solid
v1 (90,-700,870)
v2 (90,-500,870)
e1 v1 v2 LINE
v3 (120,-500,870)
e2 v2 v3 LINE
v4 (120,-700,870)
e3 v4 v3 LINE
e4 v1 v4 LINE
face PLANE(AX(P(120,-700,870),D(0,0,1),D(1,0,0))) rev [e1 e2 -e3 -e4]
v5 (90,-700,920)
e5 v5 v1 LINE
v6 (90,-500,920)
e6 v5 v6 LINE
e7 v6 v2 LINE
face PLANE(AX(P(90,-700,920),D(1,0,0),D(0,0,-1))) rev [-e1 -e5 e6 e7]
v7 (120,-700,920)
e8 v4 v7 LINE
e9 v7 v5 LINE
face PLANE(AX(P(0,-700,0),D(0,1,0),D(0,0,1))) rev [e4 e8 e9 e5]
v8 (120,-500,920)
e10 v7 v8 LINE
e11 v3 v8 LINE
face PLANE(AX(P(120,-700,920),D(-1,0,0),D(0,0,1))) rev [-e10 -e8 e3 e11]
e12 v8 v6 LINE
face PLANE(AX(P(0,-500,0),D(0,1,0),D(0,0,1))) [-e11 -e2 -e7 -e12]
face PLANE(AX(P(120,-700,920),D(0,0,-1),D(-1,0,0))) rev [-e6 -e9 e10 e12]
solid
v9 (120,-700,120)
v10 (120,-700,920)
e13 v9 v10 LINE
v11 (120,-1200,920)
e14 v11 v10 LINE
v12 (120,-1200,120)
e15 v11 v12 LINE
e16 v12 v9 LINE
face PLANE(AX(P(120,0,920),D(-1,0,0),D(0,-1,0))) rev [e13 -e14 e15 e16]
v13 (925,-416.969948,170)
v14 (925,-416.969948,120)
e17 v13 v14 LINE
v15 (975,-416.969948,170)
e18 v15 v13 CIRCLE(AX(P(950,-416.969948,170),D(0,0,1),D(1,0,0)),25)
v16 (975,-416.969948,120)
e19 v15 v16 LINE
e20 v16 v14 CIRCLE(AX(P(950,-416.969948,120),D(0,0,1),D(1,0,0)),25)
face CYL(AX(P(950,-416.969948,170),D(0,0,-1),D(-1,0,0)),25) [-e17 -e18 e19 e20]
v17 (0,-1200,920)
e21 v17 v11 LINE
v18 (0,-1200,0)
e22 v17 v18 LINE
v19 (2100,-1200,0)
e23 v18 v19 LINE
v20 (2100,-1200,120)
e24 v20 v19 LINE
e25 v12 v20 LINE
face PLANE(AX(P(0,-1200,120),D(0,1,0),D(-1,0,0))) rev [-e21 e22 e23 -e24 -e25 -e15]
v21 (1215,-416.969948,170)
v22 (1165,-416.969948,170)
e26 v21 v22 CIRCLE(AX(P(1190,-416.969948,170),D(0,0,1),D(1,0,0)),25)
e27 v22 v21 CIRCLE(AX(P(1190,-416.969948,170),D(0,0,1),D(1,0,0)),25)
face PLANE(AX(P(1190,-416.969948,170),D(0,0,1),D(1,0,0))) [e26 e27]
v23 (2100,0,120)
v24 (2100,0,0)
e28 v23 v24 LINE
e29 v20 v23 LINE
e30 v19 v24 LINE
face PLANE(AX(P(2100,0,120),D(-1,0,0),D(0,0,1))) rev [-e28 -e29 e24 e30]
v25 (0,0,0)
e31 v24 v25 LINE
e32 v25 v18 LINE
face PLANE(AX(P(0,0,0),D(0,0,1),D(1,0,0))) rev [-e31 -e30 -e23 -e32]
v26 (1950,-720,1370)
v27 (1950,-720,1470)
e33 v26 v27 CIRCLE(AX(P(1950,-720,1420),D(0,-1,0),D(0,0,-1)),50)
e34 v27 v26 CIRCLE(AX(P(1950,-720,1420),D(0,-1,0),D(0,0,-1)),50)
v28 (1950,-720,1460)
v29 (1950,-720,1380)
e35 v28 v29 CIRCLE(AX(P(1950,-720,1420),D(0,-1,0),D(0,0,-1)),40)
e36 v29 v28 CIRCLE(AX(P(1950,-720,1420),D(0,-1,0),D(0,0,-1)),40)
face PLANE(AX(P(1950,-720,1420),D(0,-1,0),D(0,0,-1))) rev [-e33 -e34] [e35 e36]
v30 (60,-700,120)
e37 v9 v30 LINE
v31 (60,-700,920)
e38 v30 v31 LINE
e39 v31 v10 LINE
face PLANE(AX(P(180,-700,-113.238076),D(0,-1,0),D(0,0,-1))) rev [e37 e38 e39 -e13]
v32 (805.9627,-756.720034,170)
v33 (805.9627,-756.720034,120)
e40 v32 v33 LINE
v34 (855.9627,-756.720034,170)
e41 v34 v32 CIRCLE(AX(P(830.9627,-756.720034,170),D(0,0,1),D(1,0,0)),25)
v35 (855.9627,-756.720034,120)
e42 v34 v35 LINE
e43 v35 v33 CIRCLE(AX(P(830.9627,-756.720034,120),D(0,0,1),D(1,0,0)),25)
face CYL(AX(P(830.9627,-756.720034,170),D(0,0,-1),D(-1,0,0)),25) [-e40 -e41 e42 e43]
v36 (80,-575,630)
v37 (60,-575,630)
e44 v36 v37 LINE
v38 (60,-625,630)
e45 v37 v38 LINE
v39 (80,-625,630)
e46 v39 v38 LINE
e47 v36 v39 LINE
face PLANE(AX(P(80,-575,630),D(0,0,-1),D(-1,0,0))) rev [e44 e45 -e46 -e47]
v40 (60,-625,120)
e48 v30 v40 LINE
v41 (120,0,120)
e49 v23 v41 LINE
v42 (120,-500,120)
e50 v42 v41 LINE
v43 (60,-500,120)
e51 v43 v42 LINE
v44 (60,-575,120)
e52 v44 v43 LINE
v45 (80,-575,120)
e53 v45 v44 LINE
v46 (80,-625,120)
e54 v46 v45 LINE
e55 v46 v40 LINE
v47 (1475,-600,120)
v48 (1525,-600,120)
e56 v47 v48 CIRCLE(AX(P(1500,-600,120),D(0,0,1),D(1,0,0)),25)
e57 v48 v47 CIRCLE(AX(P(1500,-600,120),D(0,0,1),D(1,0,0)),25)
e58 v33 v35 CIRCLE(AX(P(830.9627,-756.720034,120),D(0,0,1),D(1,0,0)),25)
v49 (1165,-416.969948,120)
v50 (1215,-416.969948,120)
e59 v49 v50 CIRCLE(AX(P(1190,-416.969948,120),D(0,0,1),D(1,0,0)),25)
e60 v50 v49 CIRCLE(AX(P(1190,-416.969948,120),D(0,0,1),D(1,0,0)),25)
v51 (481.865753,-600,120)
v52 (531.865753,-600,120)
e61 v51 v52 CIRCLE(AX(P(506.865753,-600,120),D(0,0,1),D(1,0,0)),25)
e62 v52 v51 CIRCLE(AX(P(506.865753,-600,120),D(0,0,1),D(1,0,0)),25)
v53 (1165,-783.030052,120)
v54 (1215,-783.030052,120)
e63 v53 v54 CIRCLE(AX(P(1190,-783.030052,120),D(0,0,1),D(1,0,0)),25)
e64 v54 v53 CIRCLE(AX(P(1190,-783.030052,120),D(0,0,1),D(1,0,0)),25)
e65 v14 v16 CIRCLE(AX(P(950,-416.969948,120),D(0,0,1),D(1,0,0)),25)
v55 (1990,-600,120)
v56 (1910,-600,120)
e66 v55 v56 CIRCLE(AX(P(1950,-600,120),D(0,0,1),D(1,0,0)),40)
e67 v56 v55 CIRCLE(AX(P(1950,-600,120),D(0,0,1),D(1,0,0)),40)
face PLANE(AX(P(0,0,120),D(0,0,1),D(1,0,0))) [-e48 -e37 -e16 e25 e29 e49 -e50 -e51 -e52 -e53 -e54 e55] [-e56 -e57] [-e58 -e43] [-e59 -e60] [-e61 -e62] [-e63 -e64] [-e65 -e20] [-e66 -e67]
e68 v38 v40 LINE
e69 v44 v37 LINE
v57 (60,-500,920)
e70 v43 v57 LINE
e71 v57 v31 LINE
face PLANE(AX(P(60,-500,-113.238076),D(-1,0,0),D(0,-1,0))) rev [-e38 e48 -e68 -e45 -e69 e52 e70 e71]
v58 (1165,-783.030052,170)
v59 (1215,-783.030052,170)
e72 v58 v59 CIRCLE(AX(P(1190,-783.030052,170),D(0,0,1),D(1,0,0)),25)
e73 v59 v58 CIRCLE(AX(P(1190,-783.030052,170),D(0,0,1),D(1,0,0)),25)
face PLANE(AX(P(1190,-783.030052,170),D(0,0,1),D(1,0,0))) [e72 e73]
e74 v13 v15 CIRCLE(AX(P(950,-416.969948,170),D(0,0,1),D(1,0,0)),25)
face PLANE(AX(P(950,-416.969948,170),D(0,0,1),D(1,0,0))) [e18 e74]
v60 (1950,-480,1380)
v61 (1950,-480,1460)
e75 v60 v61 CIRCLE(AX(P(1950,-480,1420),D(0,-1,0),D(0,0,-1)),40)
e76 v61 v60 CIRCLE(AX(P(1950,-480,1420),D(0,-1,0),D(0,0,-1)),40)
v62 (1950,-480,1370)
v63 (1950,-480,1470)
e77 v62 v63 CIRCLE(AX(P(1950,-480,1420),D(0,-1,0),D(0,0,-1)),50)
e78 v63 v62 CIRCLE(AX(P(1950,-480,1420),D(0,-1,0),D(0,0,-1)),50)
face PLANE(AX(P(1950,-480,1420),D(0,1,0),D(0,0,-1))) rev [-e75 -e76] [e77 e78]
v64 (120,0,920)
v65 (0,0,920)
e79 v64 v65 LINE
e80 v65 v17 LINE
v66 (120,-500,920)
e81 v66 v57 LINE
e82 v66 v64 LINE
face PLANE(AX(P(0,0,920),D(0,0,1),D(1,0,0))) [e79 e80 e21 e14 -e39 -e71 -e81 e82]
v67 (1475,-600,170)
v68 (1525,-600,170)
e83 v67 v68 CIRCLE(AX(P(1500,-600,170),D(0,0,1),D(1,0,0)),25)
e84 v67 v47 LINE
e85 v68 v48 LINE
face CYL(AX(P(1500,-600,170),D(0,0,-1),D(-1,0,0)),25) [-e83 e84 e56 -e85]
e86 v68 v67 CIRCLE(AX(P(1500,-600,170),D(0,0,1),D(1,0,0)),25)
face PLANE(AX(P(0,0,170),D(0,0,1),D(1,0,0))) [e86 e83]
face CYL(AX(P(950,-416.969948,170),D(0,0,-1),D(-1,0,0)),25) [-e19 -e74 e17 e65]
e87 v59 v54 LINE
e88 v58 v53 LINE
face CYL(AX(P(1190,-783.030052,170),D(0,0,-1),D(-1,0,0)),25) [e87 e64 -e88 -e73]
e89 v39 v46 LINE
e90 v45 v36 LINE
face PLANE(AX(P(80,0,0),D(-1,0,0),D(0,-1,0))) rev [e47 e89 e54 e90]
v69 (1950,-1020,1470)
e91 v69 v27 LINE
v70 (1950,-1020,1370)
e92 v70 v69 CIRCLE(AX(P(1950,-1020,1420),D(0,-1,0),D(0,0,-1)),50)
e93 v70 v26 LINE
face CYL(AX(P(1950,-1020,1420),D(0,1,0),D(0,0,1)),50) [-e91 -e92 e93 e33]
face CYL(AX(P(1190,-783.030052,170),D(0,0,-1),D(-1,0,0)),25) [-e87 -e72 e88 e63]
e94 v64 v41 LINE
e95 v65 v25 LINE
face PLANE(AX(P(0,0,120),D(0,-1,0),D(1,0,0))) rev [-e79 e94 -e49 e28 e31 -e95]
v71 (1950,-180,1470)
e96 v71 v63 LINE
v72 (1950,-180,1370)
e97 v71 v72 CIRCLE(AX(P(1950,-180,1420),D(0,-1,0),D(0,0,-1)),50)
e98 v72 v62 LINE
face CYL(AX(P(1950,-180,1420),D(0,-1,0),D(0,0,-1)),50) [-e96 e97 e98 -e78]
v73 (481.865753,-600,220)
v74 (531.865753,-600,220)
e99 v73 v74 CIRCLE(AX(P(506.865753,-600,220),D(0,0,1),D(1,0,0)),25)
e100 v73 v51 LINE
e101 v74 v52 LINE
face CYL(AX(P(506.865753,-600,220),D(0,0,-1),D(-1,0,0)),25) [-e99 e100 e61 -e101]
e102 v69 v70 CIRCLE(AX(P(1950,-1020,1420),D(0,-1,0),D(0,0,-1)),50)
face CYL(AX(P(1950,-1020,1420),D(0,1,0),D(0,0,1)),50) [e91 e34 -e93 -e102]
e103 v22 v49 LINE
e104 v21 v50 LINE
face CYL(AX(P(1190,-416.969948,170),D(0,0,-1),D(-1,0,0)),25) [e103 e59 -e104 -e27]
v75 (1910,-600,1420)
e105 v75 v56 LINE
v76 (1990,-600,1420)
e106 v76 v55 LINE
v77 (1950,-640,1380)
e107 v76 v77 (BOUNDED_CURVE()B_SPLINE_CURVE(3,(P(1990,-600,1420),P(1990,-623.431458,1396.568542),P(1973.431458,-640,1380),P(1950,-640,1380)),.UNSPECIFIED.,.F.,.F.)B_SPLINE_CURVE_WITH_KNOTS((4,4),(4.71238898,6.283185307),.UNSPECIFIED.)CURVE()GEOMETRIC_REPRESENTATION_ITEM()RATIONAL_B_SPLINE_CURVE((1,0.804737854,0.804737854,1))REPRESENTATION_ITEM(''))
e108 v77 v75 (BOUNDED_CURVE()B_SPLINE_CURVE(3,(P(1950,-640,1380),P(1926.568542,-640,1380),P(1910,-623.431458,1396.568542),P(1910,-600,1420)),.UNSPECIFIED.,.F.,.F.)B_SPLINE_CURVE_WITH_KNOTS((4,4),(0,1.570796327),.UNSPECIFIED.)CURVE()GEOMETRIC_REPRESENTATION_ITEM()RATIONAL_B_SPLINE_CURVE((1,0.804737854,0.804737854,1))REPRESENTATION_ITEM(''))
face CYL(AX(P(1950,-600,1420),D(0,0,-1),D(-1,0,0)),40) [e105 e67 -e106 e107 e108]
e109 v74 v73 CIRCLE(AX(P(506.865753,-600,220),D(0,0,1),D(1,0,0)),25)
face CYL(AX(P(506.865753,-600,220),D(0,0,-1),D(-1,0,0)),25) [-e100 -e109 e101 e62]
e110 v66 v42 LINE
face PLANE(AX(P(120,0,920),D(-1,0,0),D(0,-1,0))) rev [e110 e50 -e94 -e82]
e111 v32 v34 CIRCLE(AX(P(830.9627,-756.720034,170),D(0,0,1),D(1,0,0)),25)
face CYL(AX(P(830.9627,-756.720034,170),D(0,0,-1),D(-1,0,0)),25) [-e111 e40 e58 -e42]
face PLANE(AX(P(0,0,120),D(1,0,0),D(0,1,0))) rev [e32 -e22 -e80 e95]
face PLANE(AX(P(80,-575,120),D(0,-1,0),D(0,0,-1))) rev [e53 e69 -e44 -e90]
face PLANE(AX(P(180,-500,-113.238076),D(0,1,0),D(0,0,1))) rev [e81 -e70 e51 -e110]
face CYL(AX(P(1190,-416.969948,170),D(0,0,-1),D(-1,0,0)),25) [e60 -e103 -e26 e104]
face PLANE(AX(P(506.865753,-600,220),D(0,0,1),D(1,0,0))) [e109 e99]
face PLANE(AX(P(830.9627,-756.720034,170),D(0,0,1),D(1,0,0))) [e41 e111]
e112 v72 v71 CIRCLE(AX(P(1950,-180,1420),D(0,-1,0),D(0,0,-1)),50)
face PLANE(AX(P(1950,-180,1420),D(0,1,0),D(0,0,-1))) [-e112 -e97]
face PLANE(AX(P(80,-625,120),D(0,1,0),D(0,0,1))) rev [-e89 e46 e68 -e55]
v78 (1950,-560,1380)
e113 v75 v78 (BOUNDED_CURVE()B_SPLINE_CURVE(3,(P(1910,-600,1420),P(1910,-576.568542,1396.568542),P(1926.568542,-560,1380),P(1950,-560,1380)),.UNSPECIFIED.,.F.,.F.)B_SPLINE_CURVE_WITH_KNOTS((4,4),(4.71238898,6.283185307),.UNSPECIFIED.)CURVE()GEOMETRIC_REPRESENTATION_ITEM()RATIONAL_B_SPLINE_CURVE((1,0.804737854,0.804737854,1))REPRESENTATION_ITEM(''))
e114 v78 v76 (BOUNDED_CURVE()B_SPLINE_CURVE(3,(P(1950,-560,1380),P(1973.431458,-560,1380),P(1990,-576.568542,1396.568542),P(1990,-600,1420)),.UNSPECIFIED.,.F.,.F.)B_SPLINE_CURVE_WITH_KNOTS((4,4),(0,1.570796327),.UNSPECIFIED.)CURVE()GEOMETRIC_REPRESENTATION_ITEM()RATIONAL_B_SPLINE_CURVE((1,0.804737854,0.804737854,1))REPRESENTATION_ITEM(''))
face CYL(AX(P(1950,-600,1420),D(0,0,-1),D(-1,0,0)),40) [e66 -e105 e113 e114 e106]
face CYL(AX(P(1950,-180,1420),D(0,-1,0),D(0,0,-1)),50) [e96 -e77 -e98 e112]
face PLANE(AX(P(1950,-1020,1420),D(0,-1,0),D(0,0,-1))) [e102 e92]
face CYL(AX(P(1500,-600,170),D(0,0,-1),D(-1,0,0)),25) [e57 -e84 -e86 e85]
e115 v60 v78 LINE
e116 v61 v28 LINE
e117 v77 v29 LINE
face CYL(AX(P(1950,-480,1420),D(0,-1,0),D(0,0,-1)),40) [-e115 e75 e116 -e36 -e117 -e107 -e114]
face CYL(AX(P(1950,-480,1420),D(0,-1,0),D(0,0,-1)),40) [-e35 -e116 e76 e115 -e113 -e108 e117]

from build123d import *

# Parameters (mm, degrees)
SKETCH2_W                = 2100
SKETCH2_H                = 1200
BOSS_EXTRUDE1_DEPTH      = 120
SKETCH3_W                = 120
SKETCH3_H                = 1200
BOSS_EXTRUDE2_DEPTH      = 800
SKETCH4_R                = 40
BOSS_EXTRUDE3_DEPTH      = 1300
BOSS_EXTRUDE4_DEPTH      = 120
BOSS_EXTRUDE4_DEPTH_BACK = 120
SKETCH6_R                = 40
BOSS_EXTRUDE5_START      = 120
SKETCH7_R                = 50
BOSS_EXTRUDE5_DEPTH      = 300
SKETCH9_R                = 25
BOSS_EXTRUDE6_DEPTH      = 50
SKETCH10_R               = 25
BOSS_EXTRUDE7_DEPTH      = 50
SKETCH11_R               = 25
BOSS_EXTRUDE8_DEPTH      = 50
SKETCH12_R               = 25
BOSS_EXTRUDE9_DEPTH      = 50
SKETCH13_R               = 25
BOSS_EXTRUDE10_DEPTH     = 100
SKETCH14_W               = 120
SKETCH14_H               = 200
CUT_EXTRUDE1_DEPTH       = 800
SKETCH15_W               = 510
SKETCH15_H               = 50
BOSS_EXTRUDE11_DEPTH     = 20
SKETCH16_W               = 30
SKETCH16_H               = 50
BOSS_EXTRUDE12_DEPTH     = 200


with BuildPart() as part:
    # Sketch2 → Boss-Extrude1 (new body)
    with BuildSketch(Plane.XY):
        with Locations((1050, -600)):
            Rectangle(SKETCH2_W, SKETCH2_H)
    extrude(amount=BOSS_EXTRUDE1_DEPTH)

    # Sketch3 → Boss-Extrude2 (add)
    with BuildSketch(Plane.XY.offset(120)):
        with Locations((60, -600)):
            Rectangle(SKETCH3_W, SKETCH3_H)
    extrude(amount=BOSS_EXTRUDE2_DEPTH)

    # Sketch4 → Boss-Extrude3 (add)
    with BuildSketch(Plane.XY.offset(120)):
        with Locations((1950, -600)):
            Circle(SKETCH4_R)
    extrude(amount=BOSS_EXTRUDE3_DEPTH)

    # Sketch6 → Boss-Extrude4 (add, two sides: drawn at the far end of the back side and taken through both)
    with BuildSketch(Plane(origin=(0, -600, 0), x_dir=(-1, 0, 0), z_dir=(0, -1, 0)).offset(-BOSS_EXTRUDE4_DEPTH_BACK)):
        with Locations(Location((-1950, -1420, 0), (0, 0, 90))):
            Circle(SKETCH6_R)
    extrude(amount=BOSS_EXTRUDE4_DEPTH + BOSS_EXTRUDE4_DEPTH_BACK)

    # Sketch7 → Boss-Extrude5 (add)
    with BuildSketch(Plane(origin=(0, -600, 0), x_dir=(-1, 0, 0), z_dir=(0, -1, 0)).offset(BOSS_EXTRUDE5_START)):
        with Locations(Location((-1950, -1420, 0), (0, 0, 90))):
            Circle(SKETCH7_R)
    boss_extrude5 = extrude(amount=BOSS_EXTRUDE5_DEPTH)

    # Mirror1: Boss-Extrude5 across plane
    add(boss_extrude5.mirror(Plane(origin=(0, -600, 0), x_dir=(0, 0, 1), z_dir=(0, -1, 0))))

    # Sketch9 → Boss-Extrude6 (add)
    with BuildSketch(Plane.XY.offset(120)):
        with Locations((1500, -600)):
            Circle(SKETCH9_R)
    extrude(amount=BOSS_EXTRUDE6_DEPTH)

    # Sketch10 → Boss-Extrude7 (add)
    with BuildSketch(Plane.XY.offset(120)):
        with Locations((1190, -416.969947823)):
            Circle(SKETCH10_R)
        with Locations((1190, -783.030052177)):
            Circle(SKETCH10_R)
    extrude(amount=BOSS_EXTRUDE7_DEPTH)

    # Sketch11 → Boss-Extrude8 (add)
    with BuildSketch(Plane.XY.offset(120)):
        with Locations((950, -416.969947823)):
            Circle(SKETCH11_R)
    extrude(amount=BOSS_EXTRUDE8_DEPTH)

    # Sketch12 → Boss-Extrude9 (add)
    with BuildSketch(Plane.XY.offset(120)):
        with Locations((830.962699777, -756.720034145)):
            Circle(SKETCH12_R)
    extrude(amount=BOSS_EXTRUDE9_DEPTH)

    # Sketch13 → Boss-Extrude10 (add)
    with BuildSketch(Plane.XY.offset(120)):
        with Locations((506.86575302, -600)):
            Circle(SKETCH13_R)
    extrude(amount=BOSS_EXTRUDE10_DEPTH)

    # Sketch14 → Cut-Extrude1 (cut)
    with BuildSketch(Plane.XY.offset(920)):
        with Locations((120, -600)):
            Rectangle(SKETCH14_W, SKETCH14_H)
    extrude(amount=-CUT_EXTRUDE1_DEPTH, mode=Mode.SUBTRACT)

    # Sketch15 → Boss-Extrude11 (add)
    with BuildSketch(Plane(origin=(60, 0, 0), x_dir=(0, 0, -1), z_dir=(1, 0, 0))):
        with Locations((-375, -600)):
            Rectangle(SKETCH15_W, SKETCH15_H)
    extrude(amount=BOSS_EXTRUDE11_DEPTH)


with BuildPart() as body_2:
    # Sketch16 → Boss-Extrude12 (new body)
    with BuildSketch(Plane.XZ.offset(500)):
        with Locations((105, 895)):
            Rectangle(SKETCH16_W, SKETCH16_H)
    extrude(amount=BOSS_EXTRUDE12_DEPTH)


solid = Compound([part.part, body_2.part])
